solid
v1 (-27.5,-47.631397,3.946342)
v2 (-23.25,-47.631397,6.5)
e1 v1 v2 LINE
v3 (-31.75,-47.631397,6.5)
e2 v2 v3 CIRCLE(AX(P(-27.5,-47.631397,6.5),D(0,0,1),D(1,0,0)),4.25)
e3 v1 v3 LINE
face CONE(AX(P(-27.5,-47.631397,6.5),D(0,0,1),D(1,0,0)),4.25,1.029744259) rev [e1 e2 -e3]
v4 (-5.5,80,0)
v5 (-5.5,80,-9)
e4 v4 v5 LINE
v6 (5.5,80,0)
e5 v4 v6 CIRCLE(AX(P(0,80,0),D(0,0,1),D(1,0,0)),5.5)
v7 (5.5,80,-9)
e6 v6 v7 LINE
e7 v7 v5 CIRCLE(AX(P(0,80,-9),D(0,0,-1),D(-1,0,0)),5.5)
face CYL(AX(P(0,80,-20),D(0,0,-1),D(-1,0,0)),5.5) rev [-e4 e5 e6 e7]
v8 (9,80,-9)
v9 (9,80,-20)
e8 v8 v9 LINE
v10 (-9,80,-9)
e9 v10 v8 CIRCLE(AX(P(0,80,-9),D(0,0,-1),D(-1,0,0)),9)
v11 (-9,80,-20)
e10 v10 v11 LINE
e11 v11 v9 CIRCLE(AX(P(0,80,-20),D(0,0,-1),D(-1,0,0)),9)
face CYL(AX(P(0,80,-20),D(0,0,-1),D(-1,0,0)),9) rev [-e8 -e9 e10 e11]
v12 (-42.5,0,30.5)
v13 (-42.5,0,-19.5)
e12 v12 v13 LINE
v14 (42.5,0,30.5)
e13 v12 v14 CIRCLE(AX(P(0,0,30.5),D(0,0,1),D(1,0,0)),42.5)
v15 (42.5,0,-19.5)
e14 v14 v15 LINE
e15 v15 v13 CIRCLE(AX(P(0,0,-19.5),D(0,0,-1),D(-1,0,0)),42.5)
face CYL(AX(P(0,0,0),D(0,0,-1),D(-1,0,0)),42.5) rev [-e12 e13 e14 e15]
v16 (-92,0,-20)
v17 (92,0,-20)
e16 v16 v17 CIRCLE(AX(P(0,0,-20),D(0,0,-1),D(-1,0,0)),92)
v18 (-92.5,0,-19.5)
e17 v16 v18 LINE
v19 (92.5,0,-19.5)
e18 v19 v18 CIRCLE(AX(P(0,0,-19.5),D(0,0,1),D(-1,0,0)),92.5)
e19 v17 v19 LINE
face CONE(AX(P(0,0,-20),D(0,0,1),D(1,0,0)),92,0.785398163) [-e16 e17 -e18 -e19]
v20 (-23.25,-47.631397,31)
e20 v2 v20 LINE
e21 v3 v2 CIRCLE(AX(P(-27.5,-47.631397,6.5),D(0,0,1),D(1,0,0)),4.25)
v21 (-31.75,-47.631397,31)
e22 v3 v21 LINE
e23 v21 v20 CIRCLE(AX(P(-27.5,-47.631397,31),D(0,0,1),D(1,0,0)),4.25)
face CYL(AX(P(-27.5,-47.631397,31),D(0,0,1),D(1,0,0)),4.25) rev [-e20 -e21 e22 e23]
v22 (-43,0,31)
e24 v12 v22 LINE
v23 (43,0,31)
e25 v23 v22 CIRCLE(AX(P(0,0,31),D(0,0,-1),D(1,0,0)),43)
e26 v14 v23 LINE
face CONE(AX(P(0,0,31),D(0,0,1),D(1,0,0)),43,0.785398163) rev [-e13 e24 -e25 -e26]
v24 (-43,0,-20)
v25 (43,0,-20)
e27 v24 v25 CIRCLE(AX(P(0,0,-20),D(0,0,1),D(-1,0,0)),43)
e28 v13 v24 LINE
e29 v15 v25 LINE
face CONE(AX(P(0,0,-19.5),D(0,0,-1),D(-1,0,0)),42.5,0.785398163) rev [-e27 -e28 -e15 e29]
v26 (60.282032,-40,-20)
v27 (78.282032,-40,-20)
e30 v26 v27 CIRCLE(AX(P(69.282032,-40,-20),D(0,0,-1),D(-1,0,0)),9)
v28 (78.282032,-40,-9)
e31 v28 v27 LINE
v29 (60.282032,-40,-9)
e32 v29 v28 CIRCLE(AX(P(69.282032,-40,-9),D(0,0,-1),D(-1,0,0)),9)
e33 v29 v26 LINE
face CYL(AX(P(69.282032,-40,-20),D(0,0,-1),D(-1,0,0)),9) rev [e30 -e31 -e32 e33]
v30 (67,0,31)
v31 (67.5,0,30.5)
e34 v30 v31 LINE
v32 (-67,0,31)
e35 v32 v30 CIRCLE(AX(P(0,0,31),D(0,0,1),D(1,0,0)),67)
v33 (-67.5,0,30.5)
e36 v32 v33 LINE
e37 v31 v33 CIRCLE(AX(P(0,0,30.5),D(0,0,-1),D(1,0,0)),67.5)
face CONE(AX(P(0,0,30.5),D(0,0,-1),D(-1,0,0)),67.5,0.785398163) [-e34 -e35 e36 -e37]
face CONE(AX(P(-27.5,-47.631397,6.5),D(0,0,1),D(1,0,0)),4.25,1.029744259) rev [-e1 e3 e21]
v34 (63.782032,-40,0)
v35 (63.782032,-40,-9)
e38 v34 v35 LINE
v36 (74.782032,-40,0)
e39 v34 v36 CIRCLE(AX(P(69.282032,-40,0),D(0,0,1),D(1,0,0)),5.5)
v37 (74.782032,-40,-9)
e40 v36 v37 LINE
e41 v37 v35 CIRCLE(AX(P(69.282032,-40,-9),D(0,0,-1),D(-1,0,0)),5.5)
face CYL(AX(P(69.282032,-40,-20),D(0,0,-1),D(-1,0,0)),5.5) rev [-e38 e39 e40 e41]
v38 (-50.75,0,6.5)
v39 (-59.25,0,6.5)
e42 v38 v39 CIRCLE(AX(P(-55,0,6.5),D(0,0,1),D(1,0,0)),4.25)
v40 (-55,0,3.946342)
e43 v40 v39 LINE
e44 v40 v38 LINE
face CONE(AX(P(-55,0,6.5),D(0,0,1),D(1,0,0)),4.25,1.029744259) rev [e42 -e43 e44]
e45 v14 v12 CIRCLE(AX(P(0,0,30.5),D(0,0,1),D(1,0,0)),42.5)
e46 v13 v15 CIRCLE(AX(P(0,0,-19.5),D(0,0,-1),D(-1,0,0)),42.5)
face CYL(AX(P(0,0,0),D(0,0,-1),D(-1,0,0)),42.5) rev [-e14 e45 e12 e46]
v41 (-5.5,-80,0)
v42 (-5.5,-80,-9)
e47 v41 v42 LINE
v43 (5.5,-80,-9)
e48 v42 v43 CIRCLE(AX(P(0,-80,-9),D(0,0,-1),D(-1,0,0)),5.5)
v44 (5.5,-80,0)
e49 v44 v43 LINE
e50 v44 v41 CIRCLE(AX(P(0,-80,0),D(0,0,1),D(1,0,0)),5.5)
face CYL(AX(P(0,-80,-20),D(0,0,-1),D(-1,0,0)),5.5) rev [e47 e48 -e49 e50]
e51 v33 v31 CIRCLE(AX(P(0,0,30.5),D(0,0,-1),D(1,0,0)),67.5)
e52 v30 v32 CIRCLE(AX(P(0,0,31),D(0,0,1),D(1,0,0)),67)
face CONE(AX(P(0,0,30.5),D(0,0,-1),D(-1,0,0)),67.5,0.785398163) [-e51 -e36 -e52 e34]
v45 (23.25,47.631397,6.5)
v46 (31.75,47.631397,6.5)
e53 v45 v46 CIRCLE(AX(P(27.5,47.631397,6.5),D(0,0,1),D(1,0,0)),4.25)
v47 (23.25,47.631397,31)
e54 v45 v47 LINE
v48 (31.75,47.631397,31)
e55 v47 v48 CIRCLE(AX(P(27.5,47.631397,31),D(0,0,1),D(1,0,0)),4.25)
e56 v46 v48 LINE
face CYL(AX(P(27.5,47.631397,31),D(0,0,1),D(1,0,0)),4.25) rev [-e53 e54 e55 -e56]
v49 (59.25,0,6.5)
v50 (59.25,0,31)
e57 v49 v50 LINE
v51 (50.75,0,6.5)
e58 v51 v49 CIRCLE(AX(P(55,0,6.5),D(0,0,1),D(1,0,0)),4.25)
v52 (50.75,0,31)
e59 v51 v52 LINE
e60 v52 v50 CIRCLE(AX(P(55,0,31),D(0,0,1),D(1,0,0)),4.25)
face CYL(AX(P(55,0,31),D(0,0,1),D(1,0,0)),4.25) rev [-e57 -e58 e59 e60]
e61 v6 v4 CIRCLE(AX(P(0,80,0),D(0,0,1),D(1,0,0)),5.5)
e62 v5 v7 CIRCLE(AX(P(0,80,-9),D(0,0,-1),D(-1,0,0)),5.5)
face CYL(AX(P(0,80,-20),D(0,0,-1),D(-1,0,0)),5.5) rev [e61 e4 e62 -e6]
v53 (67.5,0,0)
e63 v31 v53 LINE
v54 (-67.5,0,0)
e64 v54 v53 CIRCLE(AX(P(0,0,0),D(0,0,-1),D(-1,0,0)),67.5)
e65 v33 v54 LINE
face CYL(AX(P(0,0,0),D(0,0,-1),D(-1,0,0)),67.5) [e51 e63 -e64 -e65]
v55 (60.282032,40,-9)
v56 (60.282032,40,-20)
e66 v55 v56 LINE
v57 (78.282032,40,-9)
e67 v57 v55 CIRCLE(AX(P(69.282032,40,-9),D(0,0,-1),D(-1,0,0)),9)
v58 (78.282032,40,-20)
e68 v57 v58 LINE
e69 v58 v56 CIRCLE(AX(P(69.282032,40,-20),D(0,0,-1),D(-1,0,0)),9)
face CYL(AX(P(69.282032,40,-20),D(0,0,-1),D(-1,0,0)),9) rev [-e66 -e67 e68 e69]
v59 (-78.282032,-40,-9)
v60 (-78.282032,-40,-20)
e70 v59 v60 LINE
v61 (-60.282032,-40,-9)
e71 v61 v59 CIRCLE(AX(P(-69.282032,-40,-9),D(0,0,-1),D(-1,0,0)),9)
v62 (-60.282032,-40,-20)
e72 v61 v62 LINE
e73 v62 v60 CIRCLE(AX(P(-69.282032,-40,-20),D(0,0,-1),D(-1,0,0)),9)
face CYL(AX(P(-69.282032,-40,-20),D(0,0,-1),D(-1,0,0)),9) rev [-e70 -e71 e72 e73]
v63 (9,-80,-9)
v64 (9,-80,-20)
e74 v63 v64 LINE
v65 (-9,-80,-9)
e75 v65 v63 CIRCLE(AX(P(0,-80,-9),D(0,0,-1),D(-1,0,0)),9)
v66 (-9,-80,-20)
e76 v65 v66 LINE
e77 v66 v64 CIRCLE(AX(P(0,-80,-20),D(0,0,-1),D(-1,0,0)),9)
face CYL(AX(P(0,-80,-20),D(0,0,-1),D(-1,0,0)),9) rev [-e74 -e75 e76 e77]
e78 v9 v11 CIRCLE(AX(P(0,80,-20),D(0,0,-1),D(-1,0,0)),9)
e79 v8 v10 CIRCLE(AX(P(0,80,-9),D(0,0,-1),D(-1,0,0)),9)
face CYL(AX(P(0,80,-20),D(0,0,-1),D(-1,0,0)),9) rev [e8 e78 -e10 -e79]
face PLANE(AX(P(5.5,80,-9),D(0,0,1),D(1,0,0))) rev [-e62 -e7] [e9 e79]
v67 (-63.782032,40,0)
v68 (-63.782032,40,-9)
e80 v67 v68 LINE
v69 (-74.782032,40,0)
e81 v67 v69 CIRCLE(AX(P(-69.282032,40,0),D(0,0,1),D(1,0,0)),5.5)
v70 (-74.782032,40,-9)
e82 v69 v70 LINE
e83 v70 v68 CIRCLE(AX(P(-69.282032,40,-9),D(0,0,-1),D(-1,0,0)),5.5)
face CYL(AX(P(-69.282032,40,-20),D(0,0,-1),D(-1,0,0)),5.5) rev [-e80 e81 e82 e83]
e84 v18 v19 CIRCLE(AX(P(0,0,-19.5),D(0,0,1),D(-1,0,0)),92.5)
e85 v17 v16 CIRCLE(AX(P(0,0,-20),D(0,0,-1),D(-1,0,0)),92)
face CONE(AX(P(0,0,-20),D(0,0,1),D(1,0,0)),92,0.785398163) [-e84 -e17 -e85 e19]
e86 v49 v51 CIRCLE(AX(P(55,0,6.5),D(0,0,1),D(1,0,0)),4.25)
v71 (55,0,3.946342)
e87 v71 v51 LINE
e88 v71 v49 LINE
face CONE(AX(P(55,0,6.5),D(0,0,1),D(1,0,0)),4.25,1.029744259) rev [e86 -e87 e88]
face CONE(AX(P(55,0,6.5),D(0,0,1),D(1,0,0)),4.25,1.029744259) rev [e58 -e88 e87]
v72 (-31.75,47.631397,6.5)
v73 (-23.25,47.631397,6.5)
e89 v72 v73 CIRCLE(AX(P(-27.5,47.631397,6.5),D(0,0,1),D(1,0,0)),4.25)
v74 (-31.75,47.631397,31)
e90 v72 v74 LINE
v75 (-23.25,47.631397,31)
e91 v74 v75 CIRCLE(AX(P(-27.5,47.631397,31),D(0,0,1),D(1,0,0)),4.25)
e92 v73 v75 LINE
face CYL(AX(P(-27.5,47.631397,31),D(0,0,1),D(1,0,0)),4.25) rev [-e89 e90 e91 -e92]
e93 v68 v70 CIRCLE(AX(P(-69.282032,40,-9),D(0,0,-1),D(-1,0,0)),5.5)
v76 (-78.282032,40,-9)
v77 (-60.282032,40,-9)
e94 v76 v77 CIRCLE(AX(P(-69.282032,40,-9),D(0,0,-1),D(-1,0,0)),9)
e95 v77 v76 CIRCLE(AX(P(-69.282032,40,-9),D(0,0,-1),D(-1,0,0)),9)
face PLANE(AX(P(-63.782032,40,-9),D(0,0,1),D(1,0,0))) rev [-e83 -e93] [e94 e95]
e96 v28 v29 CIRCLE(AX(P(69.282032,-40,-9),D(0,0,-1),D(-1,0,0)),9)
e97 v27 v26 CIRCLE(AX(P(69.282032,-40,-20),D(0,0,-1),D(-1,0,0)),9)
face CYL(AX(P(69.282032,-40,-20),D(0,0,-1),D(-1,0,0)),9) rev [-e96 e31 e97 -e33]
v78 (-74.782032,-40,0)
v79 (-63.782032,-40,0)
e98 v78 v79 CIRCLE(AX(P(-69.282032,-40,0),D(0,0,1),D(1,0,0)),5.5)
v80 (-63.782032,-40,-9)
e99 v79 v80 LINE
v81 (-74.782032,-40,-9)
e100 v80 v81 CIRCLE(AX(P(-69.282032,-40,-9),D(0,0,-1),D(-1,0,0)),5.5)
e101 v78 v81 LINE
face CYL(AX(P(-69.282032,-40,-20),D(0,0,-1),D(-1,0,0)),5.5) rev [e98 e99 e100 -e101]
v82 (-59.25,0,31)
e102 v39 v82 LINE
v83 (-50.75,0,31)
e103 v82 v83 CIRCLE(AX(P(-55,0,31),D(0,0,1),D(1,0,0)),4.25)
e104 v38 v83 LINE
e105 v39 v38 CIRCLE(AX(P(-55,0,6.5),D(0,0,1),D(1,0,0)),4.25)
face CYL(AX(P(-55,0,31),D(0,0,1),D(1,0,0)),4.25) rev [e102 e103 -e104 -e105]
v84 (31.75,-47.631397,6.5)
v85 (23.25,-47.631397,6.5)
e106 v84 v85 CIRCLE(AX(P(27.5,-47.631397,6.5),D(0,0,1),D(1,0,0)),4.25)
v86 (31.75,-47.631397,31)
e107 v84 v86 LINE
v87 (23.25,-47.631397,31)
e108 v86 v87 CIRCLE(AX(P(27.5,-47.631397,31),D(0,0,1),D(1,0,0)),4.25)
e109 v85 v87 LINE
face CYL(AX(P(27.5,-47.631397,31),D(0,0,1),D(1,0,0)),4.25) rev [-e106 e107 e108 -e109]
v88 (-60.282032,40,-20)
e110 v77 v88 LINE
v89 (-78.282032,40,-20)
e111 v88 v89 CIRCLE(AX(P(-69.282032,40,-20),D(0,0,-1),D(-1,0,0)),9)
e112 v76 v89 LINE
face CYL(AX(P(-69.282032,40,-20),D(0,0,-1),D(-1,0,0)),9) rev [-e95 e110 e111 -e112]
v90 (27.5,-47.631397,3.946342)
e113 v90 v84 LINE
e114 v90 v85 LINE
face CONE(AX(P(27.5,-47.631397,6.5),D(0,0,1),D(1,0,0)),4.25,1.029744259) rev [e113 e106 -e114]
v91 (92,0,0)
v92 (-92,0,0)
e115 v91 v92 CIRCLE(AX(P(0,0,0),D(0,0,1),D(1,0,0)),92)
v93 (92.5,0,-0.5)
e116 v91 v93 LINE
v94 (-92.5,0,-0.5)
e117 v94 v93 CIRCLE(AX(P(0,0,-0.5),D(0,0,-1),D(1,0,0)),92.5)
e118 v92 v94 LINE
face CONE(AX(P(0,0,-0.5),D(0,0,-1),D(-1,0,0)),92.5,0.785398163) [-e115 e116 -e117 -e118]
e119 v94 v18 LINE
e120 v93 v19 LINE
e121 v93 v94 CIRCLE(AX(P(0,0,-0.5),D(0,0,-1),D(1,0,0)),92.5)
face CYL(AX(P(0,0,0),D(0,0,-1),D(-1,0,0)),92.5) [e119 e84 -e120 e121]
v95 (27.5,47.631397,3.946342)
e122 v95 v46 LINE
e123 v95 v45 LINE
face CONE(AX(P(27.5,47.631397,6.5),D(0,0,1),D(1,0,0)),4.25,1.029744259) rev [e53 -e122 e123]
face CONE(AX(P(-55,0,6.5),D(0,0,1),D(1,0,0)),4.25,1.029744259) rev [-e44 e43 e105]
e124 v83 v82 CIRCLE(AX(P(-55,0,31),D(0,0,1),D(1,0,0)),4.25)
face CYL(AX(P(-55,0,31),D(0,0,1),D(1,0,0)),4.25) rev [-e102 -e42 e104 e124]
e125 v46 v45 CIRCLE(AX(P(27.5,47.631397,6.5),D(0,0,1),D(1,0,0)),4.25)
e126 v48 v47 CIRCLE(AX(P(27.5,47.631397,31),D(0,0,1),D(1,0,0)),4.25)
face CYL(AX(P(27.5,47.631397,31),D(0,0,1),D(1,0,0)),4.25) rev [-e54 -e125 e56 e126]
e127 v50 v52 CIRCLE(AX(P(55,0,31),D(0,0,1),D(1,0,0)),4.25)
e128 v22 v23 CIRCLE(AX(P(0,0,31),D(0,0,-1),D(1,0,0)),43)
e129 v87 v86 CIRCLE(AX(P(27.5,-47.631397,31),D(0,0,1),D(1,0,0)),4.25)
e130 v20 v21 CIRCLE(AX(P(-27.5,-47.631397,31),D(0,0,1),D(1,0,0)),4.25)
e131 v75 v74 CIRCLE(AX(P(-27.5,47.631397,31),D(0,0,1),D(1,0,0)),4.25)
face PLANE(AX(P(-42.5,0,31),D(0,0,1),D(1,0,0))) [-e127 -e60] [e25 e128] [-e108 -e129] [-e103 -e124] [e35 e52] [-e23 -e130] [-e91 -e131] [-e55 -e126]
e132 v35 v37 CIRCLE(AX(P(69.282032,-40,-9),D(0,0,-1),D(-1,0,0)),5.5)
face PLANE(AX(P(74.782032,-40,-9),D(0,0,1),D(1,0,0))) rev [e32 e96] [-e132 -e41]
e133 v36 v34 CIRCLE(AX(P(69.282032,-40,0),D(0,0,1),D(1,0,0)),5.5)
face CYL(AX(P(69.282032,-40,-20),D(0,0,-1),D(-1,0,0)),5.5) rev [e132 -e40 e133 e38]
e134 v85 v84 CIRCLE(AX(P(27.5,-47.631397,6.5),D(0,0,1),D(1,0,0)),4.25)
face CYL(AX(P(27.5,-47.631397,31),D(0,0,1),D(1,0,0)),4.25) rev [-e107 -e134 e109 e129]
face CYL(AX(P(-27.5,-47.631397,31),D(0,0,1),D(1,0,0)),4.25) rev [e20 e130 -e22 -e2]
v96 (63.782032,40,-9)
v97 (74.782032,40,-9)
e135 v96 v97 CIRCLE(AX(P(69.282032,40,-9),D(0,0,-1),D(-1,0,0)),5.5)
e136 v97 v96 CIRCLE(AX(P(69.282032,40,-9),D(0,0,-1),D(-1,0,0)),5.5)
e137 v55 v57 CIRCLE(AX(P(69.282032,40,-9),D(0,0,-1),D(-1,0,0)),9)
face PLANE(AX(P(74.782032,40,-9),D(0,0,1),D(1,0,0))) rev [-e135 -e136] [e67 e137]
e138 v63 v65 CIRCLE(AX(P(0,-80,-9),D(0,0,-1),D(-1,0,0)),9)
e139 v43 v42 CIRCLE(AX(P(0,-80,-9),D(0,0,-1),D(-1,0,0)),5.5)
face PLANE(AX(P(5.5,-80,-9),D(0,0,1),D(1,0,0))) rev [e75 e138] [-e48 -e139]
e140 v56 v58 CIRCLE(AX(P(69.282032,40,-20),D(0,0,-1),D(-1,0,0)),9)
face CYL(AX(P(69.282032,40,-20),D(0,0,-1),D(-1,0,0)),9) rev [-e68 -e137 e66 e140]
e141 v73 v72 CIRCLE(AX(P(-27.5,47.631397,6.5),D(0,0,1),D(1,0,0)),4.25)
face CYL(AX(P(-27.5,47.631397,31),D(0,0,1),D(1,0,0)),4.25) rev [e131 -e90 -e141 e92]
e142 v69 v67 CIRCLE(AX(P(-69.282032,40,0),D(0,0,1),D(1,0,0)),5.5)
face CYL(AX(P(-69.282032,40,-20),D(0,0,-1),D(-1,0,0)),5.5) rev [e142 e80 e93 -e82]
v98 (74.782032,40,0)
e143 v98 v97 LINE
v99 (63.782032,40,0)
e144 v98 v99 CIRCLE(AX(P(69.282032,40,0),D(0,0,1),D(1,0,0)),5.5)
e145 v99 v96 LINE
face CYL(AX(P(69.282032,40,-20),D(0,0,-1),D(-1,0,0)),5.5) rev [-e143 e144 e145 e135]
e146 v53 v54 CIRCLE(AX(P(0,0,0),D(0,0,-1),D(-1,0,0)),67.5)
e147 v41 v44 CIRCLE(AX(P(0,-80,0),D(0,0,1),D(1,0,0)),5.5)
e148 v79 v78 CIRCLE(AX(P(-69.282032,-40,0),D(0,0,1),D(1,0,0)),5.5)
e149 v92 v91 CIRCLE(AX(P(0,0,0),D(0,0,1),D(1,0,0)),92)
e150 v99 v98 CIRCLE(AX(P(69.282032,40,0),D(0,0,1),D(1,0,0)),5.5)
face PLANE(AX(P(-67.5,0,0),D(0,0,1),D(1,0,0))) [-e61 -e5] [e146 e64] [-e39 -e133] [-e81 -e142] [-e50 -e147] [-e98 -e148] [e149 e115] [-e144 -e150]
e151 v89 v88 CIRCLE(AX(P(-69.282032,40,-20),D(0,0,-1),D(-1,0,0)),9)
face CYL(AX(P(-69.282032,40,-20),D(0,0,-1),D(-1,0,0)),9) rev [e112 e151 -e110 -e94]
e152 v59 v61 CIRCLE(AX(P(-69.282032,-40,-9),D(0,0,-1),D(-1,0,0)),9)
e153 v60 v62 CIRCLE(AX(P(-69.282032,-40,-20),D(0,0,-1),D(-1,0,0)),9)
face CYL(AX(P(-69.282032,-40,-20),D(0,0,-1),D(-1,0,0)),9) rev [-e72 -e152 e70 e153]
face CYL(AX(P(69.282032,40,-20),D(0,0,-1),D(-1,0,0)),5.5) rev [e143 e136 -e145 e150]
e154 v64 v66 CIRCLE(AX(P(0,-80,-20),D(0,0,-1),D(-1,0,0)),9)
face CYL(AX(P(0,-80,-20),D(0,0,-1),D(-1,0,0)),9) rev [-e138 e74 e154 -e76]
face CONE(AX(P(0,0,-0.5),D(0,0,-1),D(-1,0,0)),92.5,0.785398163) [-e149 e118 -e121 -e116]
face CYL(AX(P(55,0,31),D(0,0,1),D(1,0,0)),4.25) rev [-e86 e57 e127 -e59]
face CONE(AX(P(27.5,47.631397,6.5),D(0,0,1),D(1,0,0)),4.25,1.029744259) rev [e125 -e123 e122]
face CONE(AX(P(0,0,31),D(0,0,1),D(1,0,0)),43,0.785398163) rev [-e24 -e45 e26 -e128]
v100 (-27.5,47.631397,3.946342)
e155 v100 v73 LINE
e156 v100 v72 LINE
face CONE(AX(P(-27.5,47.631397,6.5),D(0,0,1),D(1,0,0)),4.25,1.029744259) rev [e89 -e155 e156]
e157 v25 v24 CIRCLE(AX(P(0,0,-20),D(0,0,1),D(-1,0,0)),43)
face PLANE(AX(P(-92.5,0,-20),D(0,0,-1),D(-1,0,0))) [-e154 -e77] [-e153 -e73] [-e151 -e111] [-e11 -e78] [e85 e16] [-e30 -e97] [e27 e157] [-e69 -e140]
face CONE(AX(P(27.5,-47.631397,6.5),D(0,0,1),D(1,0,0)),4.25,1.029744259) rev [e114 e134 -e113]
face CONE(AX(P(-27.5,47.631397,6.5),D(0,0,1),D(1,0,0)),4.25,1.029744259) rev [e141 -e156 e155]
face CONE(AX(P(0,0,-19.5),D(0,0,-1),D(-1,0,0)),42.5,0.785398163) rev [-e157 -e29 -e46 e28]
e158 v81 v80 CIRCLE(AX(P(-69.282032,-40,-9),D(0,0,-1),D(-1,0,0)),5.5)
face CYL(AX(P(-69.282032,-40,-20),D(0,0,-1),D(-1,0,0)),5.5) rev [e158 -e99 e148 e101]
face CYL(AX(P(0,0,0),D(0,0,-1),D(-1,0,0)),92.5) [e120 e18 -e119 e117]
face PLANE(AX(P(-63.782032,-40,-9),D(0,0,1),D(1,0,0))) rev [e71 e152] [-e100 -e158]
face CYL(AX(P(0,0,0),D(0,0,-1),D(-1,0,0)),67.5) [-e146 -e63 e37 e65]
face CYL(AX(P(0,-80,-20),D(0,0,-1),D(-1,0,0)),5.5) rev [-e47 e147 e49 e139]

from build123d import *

# Parameters (mm, degrees)
HOLE_WIZARD_1_D           = 11
HOLE_WIZARD_1_CBORE_D     = 18
HOLE_WIZARD_1_CBORE_DEPTH = 11
PATTERN_CIRCULAR_1_COUNT  = 6
PATTERN_CIRCULAR_2_COUNT  = 6
CHAMFER_1_SIZE            = 0.5


with BuildPart() as part:
    # 草图1 → 旋转1 (revolve)
    with BuildSketch(Plane(origin=(0, 0, 0), x_dir=(1, 0, 0), z_dir=(0, 1, 0))):
        Polygon((-42.5, 20), (-42.5, -31), (-67.5, -31), (-67.5, 0), (-92.5, 0), (-92.5, 20), align=None)
    revolve(axis=Axis((0, 0, 0), (0, 0, 1)))

    # 打孔尺寸(%根据)内六角圆柱头螺钉的类型1 (through all)
    with Locations(Plane(origin=(0, 0, -20), x_dir=(1, 0, 0), z_dir=(0, 0, -1))):
        with Locations((0, 80)):
            hole_wizard_1 = CounterBoreHole(HOLE_WIZARD_1_D / 2, HOLE_WIZARD_1_CBORE_D / 2, HOLE_WIZARD_1_CBORE_DEPTH)

    # 阵列(圆周)1: 打孔尺寸(%根据)内六角圆柱头螺钉的类型1 ×6 about axis
    pattern_circular_1_axis = Axis((0, 0, 0), (0, 0, 1))
    for i in range(1, PATTERN_CIRCULAR_1_COUNT):
        add(hole_wizard_1.rotate(pattern_circular_1_axis, i * 360 / PATTERN_CIRCULAR_1_COUNT), mode=Mode.SUBTRACT)

    # 草图7 → M10 螺纹孔1 (revolve, cut)
    with BuildSketch(Plane(origin=(-55, 0, 31), x_dir=(0, -1, 0), z_dir=(1, 0, 0))):
        Polygon((0, 0), (0, 27.053657631), (4.25, 24.5), (4.25, 0), align=None)
    hole_wizard_m10_1 = revolve(axis=Axis((-55, 0, 37.35), (0, 0, -1)), mode=Mode.SUBTRACT)

    # 阵列(圆周)2: M10 螺纹孔1 ×6 about axis
    pattern_circular_2_axis = Axis((0, 0, 0), (0, 0, 1))
    for i in range(1, PATTERN_CIRCULAR_2_COUNT):
        add(hole_wizard_m10_1.rotate(pattern_circular_2_axis, i * 360 / PATTERN_CIRCULAR_2_COUNT), mode=Mode.SUBTRACT)

    # 倒角1
    chamfer_1_edges = [part.edges().sort_by_distance(p)[0] for p in [
        (42.5, 0, 31),
        (42.5, 0, -20),
        (92.5, 0, -20),
        (92.5, 0, 0),
        (67.5, 0, 31),
    ]]
    chamfer(chamfer_1_edges, length=CHAMFER_1_SIZE)


solid = part.part
